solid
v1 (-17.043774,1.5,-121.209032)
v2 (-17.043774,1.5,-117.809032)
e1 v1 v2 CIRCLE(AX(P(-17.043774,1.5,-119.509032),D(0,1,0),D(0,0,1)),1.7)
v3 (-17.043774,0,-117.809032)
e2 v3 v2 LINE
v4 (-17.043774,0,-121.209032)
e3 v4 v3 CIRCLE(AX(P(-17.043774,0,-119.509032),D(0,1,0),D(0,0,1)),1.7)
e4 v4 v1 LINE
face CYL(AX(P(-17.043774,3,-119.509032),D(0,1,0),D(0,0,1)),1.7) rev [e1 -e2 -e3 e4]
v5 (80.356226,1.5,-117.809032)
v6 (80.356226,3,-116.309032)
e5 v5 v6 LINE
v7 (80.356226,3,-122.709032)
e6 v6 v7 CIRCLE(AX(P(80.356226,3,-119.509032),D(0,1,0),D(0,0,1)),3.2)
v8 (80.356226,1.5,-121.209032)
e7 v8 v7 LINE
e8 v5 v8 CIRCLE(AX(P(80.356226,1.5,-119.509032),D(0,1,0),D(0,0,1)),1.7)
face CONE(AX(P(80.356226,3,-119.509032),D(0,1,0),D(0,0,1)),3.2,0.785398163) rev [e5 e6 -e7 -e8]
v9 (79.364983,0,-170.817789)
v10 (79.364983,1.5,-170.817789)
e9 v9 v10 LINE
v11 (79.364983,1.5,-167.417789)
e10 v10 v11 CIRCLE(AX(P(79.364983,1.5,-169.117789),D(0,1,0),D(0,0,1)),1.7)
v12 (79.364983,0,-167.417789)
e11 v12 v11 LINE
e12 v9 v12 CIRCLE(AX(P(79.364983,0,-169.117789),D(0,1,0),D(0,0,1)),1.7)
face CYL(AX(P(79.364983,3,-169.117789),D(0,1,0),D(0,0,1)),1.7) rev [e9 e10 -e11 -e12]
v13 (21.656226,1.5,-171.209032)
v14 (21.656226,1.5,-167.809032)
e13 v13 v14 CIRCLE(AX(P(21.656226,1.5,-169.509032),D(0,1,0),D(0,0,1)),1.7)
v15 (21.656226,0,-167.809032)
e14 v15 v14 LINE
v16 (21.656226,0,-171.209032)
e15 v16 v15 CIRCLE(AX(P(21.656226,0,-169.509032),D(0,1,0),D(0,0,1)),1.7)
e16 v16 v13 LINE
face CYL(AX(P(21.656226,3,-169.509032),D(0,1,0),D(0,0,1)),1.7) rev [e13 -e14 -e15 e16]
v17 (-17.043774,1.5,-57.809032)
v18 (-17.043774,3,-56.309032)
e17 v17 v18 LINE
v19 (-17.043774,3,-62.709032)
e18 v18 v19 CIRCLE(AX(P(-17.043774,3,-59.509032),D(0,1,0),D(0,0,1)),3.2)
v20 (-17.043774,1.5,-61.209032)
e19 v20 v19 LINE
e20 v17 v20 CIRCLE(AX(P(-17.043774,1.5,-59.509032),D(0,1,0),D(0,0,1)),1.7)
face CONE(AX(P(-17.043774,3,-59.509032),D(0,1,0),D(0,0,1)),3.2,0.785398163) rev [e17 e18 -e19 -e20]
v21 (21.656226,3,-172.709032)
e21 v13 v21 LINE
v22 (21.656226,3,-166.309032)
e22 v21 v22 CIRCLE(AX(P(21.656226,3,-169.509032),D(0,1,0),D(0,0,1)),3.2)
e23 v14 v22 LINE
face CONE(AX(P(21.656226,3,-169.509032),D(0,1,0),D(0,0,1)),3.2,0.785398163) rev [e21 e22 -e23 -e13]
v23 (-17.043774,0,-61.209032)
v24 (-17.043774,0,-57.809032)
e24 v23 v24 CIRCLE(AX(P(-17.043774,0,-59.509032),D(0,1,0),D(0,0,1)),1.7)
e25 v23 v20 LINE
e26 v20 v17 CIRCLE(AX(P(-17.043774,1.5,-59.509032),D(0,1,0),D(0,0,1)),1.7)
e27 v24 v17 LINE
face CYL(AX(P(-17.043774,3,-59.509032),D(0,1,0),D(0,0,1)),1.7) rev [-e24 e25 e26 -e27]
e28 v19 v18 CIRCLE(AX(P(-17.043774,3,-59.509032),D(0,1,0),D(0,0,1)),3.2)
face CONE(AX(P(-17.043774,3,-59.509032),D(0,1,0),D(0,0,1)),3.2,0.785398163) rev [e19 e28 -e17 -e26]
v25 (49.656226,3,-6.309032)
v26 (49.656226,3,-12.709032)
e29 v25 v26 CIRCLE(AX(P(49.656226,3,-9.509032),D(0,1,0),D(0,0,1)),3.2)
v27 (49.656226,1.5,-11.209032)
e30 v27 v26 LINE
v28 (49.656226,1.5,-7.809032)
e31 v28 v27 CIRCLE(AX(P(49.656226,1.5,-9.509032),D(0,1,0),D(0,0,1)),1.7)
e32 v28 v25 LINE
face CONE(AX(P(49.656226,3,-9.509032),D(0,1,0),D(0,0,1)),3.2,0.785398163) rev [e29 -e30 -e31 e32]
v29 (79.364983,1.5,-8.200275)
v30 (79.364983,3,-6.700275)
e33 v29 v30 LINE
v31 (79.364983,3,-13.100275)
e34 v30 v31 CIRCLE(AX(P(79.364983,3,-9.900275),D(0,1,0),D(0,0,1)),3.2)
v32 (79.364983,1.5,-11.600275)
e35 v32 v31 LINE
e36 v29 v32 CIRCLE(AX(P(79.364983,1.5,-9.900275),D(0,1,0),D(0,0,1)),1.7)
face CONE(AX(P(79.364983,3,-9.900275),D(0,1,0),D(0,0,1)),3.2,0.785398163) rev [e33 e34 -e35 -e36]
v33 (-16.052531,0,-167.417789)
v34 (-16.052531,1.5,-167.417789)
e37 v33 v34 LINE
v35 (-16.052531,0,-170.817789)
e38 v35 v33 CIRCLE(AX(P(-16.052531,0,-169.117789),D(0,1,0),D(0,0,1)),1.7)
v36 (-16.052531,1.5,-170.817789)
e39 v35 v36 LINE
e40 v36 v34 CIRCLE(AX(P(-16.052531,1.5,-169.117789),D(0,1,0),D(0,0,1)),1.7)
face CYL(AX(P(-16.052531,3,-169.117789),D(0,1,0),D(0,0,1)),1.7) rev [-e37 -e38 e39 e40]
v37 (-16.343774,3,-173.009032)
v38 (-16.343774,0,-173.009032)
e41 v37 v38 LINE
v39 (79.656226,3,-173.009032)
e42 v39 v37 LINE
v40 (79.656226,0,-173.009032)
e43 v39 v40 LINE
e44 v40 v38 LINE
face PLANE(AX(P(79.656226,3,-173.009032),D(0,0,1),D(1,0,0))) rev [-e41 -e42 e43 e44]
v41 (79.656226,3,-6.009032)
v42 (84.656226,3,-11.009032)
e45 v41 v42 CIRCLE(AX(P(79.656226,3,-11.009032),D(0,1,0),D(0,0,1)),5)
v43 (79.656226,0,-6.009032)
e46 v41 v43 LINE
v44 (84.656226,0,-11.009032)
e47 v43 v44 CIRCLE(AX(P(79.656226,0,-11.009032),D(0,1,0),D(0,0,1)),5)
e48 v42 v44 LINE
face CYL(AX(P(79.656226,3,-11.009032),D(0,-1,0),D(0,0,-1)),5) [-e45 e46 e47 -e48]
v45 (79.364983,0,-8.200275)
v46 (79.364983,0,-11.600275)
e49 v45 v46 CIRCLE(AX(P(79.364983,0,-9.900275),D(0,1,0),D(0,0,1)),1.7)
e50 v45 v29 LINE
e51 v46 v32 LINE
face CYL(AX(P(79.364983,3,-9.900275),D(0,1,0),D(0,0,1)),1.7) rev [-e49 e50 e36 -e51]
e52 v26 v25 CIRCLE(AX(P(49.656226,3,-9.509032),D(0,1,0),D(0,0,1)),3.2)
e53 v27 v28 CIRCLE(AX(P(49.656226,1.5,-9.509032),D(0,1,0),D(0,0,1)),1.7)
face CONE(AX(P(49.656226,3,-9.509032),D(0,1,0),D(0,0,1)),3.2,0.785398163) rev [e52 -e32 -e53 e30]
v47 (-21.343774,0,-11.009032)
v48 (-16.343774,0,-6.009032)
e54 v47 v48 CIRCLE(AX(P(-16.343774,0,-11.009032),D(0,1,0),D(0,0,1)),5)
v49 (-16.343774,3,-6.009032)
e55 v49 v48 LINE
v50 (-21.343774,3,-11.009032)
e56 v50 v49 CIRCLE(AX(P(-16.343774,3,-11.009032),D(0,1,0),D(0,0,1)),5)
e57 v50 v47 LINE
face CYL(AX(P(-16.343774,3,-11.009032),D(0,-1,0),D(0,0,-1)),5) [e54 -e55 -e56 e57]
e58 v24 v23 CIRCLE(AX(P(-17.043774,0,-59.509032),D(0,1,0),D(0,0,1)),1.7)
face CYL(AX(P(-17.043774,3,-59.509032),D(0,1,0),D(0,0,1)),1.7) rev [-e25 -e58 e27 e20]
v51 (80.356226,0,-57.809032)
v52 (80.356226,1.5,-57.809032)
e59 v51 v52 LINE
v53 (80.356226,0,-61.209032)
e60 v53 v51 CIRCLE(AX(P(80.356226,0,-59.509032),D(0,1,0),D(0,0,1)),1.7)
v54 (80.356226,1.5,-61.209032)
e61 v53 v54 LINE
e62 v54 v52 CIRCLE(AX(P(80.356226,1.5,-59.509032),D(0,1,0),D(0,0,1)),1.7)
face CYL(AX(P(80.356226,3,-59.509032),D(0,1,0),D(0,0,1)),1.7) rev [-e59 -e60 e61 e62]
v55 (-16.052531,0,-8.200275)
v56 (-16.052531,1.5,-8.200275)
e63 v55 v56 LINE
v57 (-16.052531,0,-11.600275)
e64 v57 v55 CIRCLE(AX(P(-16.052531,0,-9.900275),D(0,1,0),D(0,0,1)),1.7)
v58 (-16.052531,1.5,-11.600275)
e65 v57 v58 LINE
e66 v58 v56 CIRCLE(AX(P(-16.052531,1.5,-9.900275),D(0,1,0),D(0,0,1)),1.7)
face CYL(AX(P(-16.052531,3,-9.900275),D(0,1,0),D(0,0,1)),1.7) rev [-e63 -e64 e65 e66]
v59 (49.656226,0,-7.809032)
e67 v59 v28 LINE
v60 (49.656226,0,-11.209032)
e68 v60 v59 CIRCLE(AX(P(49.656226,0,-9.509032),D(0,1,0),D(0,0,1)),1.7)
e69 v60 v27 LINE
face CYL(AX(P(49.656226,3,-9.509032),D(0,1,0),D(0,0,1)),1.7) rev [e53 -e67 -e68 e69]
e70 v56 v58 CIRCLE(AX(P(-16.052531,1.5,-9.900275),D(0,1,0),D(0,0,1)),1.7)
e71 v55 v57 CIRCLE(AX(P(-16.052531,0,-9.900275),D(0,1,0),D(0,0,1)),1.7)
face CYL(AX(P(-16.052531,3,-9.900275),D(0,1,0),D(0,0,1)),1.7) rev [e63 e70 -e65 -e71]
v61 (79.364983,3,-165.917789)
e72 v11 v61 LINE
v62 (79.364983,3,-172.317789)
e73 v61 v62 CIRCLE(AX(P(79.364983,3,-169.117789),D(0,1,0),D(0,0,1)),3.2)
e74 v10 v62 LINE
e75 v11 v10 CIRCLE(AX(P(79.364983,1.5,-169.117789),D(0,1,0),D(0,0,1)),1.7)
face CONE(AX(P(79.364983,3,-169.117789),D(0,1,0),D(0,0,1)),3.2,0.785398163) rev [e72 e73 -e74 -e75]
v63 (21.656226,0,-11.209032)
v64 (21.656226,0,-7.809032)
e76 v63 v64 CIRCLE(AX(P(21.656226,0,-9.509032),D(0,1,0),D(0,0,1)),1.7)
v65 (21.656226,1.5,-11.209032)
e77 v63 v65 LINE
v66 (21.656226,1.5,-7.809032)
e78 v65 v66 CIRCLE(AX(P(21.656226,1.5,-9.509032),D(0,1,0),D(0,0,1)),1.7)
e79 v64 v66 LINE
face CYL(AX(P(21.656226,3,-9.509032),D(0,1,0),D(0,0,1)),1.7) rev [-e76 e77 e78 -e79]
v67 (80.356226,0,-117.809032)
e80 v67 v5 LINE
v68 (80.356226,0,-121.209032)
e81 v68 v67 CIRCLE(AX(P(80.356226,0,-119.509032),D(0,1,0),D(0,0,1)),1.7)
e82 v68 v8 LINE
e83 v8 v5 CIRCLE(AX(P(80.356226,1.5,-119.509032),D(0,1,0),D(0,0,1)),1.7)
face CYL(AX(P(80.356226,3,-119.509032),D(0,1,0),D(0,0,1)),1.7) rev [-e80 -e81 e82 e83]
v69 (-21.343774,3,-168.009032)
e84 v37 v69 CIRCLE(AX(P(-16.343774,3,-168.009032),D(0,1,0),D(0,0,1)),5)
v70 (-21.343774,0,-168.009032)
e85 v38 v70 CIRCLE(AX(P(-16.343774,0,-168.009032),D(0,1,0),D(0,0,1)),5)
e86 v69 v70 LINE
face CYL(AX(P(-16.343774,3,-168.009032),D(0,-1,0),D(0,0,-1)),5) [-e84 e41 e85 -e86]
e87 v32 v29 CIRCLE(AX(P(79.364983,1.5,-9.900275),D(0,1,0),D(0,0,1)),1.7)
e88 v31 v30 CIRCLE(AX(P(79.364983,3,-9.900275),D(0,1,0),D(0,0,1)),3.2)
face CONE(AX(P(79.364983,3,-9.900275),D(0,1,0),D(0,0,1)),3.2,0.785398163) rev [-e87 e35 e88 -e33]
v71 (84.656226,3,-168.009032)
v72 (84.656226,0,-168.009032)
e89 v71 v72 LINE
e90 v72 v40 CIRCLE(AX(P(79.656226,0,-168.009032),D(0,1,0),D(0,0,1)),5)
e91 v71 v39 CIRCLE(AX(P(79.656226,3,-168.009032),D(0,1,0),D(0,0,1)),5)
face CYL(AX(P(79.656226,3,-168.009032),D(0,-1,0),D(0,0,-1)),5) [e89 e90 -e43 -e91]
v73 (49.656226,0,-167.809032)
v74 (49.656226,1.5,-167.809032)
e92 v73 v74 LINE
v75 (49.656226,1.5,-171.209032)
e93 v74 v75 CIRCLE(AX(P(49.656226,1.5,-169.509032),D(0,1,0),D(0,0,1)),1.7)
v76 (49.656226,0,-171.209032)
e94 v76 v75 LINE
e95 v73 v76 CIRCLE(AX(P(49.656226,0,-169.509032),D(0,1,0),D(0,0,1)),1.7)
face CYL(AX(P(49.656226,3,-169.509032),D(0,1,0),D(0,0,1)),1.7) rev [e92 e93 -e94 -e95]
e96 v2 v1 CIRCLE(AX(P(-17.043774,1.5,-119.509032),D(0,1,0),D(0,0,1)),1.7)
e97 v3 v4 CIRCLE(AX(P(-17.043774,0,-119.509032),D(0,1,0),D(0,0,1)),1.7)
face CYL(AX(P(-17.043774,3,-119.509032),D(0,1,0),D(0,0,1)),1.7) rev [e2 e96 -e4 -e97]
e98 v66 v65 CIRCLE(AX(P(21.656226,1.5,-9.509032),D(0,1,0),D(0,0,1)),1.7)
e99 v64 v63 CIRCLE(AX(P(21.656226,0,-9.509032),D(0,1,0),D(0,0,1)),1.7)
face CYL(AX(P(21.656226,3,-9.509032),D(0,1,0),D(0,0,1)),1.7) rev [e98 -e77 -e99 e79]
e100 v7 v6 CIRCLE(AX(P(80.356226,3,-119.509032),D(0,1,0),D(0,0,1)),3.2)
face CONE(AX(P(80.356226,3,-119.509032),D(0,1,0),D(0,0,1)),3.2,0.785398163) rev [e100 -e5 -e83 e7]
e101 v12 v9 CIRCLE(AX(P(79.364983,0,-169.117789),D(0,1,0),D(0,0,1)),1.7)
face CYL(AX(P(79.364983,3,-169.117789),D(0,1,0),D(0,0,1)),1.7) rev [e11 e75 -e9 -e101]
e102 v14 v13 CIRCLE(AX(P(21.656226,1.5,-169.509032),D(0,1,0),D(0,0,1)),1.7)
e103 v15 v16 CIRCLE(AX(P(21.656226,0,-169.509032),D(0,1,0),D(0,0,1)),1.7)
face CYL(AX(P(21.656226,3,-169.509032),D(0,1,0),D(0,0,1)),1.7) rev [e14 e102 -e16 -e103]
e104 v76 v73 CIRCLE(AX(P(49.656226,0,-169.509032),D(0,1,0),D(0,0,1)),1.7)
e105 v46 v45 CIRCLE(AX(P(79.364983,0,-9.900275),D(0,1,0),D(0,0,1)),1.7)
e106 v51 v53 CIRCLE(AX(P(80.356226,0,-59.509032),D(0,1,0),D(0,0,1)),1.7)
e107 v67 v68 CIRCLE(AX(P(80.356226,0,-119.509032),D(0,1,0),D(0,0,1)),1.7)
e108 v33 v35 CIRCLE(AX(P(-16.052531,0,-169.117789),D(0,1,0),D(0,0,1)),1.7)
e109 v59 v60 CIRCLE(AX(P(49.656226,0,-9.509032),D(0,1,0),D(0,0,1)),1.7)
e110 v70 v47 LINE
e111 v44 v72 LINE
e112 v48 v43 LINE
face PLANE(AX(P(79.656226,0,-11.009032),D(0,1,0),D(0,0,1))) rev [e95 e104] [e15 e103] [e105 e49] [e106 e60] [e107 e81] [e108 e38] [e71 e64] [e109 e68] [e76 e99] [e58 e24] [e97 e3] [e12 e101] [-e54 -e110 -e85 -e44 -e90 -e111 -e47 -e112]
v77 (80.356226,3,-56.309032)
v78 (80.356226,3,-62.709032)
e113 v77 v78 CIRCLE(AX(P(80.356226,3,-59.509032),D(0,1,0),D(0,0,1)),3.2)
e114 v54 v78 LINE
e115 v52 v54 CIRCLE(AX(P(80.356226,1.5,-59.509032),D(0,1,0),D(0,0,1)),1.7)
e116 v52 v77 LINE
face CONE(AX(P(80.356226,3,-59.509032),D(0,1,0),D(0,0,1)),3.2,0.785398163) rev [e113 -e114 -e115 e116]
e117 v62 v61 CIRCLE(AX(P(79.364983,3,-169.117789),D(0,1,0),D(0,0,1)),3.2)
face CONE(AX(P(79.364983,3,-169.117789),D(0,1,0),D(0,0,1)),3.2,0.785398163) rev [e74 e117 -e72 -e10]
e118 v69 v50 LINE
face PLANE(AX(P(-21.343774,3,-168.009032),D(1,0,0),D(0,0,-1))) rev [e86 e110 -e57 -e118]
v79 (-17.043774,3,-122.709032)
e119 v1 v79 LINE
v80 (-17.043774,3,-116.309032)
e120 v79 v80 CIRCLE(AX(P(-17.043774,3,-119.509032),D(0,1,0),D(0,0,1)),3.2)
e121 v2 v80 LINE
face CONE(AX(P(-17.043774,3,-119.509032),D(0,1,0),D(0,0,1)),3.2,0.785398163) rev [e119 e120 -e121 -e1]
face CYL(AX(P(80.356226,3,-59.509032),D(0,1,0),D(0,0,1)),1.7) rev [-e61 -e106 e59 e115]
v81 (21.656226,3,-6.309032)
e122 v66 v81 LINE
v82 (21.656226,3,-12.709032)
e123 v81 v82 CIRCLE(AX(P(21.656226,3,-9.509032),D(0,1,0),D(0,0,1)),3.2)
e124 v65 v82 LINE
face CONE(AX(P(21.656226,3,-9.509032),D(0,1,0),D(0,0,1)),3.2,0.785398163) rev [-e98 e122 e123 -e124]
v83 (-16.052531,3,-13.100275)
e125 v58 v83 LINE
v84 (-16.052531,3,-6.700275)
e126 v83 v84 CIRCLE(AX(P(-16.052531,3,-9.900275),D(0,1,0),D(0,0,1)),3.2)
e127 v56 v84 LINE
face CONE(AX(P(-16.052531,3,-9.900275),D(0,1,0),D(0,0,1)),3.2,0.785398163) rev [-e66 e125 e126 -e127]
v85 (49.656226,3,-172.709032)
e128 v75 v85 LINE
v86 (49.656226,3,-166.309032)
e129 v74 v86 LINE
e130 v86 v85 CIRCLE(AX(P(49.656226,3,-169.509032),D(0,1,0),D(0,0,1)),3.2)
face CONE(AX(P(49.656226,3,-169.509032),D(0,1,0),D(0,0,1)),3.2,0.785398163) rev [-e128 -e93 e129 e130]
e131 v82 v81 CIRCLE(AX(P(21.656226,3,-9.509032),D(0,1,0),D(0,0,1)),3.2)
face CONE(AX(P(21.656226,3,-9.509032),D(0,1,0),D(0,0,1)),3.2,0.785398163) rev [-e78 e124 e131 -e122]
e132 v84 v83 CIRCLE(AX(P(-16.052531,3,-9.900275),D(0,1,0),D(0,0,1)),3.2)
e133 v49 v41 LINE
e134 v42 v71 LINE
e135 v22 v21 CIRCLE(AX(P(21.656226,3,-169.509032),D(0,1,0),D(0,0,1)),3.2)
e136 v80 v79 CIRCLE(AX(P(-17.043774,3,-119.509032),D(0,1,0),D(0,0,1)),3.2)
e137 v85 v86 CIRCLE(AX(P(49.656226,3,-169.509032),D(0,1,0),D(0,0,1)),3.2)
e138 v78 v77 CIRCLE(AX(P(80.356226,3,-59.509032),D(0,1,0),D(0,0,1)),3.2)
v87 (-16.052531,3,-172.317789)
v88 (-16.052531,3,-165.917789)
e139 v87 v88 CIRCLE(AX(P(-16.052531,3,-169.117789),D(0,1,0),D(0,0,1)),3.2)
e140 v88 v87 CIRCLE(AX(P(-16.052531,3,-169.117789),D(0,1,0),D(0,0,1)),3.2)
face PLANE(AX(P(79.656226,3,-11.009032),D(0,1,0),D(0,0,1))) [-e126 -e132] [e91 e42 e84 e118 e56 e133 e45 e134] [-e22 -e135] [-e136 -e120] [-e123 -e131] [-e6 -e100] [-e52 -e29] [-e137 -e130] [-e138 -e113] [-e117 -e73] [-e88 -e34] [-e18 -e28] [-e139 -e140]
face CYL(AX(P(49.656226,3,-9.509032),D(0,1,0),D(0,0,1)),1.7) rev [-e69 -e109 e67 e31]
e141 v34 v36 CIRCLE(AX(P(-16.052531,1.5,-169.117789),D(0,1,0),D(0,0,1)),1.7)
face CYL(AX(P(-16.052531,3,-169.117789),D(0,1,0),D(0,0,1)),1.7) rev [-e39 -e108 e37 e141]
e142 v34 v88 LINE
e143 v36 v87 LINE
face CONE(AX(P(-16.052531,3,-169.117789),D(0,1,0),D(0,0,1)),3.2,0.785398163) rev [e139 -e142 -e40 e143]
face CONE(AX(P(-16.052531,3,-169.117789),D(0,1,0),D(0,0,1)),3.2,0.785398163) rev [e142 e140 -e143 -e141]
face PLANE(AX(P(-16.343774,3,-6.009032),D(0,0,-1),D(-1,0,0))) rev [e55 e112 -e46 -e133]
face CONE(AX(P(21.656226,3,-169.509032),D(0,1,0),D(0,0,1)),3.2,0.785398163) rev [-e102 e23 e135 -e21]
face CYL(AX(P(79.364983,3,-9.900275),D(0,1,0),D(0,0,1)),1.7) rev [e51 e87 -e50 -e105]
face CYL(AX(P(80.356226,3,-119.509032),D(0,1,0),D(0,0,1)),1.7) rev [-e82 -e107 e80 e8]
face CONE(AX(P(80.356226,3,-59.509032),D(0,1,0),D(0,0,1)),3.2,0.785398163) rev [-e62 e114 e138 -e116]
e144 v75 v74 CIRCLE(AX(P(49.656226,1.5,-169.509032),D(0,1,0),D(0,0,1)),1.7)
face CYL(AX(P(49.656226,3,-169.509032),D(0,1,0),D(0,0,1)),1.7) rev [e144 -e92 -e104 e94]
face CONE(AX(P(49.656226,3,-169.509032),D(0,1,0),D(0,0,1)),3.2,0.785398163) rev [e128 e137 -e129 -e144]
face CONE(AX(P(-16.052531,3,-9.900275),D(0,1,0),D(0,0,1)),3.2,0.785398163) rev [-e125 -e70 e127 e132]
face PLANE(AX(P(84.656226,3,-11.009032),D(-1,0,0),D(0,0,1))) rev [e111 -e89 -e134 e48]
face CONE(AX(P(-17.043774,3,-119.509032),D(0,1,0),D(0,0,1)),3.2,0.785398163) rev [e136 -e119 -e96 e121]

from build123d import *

# Parameters (mm, degrees)
BOSS_EXTRUDE1_DEPTH                                  = 3
HOLE_SIZE_FOR_SLOTTED_COUNTERSUNK_HEAD_S_D           = 3.4
HOLE_SIZE_FOR_SLOTTED_COUNTERSUNK_HEAD_S_DEPTH       = 13.5
HOLE_SIZE_FOR_SLOTTED_COUNTERSUNK_HEAD_S_CSINK_D     = 6.4
HOLE_SIZE_FOR_SLOTTED_COUNTERSUNK_HEAD_S_CSINK_ANGLE = 90
HOLE_SIZE_FOR_SLOTTED_COUNTERSUNK_HEAD_S_TIP         = 1.021463052


with BuildPart() as part:
    # Sketch1 → Boss-Extrude1 (new body)
    with BuildSketch(Plane(origin=(0, 0, 0), x_dir=(1, 0, 0), z_dir=(0, 1, 0))):
        with BuildLine():
            Line((84.656225745, 11.009032059), (84.656225745, 168.009032059))
            ThreePointArc((84.656225745, 168.009032059), (83.191759651, 171.544565965), (79.656225745, 173.009032059))
            Line((79.656225745, 173.009032059), (-16.343774255, 173.009032059))
            ThreePointArc((-16.343774255, 173.009032059), (-19.879308161, 171.544565965), (-21.343774255, 168.009032059))
            Line((-21.343774255, 168.009032059), (-21.343774255, 11.009032059))
            ThreePointArc((-21.343774255, 11.009032059), (-19.879308161, 7.473498153), (-16.343774255, 6.009032059))
            Line((-16.343774255, 6.009032059), (79.656225745, 6.009032059))
            ThreePointArc((79.656225745, 6.009032059), (83.191759651, 7.473498153), (84.656225745, 11.009032059))
        make_face()
    extrude(amount=BOSS_EXTRUDE1_DEPTH)

    # Hole size for slotted countersunk head screw type 0
    with Locations(Plane(origin=(0, 3, 0), x_dir=(1, 0, 0), z_dir=(0, 1, 0))):
        with Locations((-16.052531466, 169.11778927), (79.364982956, 169.11778927), (80.356225745, 119.509032059), (80.356225745, 59.509032059), (79.364982956, 9.900274848), (-16.052531466, 9.900274848), (-17.043774255, 59.509032059), (-17.043774255, 119.509032059), (21.656225745, 169.509032059), (49.656225745, 169.509032059), (21.656225745, 9.509032059), (49.656225745, 9.509032059)):
            CounterSinkHole(HOLE_SIZE_FOR_SLOTTED_COUNTERSUNK_HEAD_S_D / 2, HOLE_SIZE_FOR_SLOTTED_COUNTERSUNK_HEAD_S_CSINK_D / 2, depth=HOLE_SIZE_FOR_SLOTTED_COUNTERSUNK_HEAD_S_DEPTH, counter_sink_angle=HOLE_SIZE_FOR_SLOTTED_COUNTERSUNK_HEAD_S_CSINK_ANGLE)
            with Locations((0, 0, -(HOLE_SIZE_FOR_SLOTTED_COUNTERSUNK_HEAD_S_DEPTH + HOLE_SIZE_FOR_SLOTTED_COUNTERSUNK_HEAD_S_TIP / 2))):  # 118° drill point
                Cone(0, HOLE_SIZE_FOR_SLOTTED_COUNTERSUNK_HEAD_S_D / 2, HOLE_SIZE_FOR_SLOTTED_COUNTERSUNK_HEAD_S_TIP, mode=Mode.SUBTRACT)


solid = part.part
